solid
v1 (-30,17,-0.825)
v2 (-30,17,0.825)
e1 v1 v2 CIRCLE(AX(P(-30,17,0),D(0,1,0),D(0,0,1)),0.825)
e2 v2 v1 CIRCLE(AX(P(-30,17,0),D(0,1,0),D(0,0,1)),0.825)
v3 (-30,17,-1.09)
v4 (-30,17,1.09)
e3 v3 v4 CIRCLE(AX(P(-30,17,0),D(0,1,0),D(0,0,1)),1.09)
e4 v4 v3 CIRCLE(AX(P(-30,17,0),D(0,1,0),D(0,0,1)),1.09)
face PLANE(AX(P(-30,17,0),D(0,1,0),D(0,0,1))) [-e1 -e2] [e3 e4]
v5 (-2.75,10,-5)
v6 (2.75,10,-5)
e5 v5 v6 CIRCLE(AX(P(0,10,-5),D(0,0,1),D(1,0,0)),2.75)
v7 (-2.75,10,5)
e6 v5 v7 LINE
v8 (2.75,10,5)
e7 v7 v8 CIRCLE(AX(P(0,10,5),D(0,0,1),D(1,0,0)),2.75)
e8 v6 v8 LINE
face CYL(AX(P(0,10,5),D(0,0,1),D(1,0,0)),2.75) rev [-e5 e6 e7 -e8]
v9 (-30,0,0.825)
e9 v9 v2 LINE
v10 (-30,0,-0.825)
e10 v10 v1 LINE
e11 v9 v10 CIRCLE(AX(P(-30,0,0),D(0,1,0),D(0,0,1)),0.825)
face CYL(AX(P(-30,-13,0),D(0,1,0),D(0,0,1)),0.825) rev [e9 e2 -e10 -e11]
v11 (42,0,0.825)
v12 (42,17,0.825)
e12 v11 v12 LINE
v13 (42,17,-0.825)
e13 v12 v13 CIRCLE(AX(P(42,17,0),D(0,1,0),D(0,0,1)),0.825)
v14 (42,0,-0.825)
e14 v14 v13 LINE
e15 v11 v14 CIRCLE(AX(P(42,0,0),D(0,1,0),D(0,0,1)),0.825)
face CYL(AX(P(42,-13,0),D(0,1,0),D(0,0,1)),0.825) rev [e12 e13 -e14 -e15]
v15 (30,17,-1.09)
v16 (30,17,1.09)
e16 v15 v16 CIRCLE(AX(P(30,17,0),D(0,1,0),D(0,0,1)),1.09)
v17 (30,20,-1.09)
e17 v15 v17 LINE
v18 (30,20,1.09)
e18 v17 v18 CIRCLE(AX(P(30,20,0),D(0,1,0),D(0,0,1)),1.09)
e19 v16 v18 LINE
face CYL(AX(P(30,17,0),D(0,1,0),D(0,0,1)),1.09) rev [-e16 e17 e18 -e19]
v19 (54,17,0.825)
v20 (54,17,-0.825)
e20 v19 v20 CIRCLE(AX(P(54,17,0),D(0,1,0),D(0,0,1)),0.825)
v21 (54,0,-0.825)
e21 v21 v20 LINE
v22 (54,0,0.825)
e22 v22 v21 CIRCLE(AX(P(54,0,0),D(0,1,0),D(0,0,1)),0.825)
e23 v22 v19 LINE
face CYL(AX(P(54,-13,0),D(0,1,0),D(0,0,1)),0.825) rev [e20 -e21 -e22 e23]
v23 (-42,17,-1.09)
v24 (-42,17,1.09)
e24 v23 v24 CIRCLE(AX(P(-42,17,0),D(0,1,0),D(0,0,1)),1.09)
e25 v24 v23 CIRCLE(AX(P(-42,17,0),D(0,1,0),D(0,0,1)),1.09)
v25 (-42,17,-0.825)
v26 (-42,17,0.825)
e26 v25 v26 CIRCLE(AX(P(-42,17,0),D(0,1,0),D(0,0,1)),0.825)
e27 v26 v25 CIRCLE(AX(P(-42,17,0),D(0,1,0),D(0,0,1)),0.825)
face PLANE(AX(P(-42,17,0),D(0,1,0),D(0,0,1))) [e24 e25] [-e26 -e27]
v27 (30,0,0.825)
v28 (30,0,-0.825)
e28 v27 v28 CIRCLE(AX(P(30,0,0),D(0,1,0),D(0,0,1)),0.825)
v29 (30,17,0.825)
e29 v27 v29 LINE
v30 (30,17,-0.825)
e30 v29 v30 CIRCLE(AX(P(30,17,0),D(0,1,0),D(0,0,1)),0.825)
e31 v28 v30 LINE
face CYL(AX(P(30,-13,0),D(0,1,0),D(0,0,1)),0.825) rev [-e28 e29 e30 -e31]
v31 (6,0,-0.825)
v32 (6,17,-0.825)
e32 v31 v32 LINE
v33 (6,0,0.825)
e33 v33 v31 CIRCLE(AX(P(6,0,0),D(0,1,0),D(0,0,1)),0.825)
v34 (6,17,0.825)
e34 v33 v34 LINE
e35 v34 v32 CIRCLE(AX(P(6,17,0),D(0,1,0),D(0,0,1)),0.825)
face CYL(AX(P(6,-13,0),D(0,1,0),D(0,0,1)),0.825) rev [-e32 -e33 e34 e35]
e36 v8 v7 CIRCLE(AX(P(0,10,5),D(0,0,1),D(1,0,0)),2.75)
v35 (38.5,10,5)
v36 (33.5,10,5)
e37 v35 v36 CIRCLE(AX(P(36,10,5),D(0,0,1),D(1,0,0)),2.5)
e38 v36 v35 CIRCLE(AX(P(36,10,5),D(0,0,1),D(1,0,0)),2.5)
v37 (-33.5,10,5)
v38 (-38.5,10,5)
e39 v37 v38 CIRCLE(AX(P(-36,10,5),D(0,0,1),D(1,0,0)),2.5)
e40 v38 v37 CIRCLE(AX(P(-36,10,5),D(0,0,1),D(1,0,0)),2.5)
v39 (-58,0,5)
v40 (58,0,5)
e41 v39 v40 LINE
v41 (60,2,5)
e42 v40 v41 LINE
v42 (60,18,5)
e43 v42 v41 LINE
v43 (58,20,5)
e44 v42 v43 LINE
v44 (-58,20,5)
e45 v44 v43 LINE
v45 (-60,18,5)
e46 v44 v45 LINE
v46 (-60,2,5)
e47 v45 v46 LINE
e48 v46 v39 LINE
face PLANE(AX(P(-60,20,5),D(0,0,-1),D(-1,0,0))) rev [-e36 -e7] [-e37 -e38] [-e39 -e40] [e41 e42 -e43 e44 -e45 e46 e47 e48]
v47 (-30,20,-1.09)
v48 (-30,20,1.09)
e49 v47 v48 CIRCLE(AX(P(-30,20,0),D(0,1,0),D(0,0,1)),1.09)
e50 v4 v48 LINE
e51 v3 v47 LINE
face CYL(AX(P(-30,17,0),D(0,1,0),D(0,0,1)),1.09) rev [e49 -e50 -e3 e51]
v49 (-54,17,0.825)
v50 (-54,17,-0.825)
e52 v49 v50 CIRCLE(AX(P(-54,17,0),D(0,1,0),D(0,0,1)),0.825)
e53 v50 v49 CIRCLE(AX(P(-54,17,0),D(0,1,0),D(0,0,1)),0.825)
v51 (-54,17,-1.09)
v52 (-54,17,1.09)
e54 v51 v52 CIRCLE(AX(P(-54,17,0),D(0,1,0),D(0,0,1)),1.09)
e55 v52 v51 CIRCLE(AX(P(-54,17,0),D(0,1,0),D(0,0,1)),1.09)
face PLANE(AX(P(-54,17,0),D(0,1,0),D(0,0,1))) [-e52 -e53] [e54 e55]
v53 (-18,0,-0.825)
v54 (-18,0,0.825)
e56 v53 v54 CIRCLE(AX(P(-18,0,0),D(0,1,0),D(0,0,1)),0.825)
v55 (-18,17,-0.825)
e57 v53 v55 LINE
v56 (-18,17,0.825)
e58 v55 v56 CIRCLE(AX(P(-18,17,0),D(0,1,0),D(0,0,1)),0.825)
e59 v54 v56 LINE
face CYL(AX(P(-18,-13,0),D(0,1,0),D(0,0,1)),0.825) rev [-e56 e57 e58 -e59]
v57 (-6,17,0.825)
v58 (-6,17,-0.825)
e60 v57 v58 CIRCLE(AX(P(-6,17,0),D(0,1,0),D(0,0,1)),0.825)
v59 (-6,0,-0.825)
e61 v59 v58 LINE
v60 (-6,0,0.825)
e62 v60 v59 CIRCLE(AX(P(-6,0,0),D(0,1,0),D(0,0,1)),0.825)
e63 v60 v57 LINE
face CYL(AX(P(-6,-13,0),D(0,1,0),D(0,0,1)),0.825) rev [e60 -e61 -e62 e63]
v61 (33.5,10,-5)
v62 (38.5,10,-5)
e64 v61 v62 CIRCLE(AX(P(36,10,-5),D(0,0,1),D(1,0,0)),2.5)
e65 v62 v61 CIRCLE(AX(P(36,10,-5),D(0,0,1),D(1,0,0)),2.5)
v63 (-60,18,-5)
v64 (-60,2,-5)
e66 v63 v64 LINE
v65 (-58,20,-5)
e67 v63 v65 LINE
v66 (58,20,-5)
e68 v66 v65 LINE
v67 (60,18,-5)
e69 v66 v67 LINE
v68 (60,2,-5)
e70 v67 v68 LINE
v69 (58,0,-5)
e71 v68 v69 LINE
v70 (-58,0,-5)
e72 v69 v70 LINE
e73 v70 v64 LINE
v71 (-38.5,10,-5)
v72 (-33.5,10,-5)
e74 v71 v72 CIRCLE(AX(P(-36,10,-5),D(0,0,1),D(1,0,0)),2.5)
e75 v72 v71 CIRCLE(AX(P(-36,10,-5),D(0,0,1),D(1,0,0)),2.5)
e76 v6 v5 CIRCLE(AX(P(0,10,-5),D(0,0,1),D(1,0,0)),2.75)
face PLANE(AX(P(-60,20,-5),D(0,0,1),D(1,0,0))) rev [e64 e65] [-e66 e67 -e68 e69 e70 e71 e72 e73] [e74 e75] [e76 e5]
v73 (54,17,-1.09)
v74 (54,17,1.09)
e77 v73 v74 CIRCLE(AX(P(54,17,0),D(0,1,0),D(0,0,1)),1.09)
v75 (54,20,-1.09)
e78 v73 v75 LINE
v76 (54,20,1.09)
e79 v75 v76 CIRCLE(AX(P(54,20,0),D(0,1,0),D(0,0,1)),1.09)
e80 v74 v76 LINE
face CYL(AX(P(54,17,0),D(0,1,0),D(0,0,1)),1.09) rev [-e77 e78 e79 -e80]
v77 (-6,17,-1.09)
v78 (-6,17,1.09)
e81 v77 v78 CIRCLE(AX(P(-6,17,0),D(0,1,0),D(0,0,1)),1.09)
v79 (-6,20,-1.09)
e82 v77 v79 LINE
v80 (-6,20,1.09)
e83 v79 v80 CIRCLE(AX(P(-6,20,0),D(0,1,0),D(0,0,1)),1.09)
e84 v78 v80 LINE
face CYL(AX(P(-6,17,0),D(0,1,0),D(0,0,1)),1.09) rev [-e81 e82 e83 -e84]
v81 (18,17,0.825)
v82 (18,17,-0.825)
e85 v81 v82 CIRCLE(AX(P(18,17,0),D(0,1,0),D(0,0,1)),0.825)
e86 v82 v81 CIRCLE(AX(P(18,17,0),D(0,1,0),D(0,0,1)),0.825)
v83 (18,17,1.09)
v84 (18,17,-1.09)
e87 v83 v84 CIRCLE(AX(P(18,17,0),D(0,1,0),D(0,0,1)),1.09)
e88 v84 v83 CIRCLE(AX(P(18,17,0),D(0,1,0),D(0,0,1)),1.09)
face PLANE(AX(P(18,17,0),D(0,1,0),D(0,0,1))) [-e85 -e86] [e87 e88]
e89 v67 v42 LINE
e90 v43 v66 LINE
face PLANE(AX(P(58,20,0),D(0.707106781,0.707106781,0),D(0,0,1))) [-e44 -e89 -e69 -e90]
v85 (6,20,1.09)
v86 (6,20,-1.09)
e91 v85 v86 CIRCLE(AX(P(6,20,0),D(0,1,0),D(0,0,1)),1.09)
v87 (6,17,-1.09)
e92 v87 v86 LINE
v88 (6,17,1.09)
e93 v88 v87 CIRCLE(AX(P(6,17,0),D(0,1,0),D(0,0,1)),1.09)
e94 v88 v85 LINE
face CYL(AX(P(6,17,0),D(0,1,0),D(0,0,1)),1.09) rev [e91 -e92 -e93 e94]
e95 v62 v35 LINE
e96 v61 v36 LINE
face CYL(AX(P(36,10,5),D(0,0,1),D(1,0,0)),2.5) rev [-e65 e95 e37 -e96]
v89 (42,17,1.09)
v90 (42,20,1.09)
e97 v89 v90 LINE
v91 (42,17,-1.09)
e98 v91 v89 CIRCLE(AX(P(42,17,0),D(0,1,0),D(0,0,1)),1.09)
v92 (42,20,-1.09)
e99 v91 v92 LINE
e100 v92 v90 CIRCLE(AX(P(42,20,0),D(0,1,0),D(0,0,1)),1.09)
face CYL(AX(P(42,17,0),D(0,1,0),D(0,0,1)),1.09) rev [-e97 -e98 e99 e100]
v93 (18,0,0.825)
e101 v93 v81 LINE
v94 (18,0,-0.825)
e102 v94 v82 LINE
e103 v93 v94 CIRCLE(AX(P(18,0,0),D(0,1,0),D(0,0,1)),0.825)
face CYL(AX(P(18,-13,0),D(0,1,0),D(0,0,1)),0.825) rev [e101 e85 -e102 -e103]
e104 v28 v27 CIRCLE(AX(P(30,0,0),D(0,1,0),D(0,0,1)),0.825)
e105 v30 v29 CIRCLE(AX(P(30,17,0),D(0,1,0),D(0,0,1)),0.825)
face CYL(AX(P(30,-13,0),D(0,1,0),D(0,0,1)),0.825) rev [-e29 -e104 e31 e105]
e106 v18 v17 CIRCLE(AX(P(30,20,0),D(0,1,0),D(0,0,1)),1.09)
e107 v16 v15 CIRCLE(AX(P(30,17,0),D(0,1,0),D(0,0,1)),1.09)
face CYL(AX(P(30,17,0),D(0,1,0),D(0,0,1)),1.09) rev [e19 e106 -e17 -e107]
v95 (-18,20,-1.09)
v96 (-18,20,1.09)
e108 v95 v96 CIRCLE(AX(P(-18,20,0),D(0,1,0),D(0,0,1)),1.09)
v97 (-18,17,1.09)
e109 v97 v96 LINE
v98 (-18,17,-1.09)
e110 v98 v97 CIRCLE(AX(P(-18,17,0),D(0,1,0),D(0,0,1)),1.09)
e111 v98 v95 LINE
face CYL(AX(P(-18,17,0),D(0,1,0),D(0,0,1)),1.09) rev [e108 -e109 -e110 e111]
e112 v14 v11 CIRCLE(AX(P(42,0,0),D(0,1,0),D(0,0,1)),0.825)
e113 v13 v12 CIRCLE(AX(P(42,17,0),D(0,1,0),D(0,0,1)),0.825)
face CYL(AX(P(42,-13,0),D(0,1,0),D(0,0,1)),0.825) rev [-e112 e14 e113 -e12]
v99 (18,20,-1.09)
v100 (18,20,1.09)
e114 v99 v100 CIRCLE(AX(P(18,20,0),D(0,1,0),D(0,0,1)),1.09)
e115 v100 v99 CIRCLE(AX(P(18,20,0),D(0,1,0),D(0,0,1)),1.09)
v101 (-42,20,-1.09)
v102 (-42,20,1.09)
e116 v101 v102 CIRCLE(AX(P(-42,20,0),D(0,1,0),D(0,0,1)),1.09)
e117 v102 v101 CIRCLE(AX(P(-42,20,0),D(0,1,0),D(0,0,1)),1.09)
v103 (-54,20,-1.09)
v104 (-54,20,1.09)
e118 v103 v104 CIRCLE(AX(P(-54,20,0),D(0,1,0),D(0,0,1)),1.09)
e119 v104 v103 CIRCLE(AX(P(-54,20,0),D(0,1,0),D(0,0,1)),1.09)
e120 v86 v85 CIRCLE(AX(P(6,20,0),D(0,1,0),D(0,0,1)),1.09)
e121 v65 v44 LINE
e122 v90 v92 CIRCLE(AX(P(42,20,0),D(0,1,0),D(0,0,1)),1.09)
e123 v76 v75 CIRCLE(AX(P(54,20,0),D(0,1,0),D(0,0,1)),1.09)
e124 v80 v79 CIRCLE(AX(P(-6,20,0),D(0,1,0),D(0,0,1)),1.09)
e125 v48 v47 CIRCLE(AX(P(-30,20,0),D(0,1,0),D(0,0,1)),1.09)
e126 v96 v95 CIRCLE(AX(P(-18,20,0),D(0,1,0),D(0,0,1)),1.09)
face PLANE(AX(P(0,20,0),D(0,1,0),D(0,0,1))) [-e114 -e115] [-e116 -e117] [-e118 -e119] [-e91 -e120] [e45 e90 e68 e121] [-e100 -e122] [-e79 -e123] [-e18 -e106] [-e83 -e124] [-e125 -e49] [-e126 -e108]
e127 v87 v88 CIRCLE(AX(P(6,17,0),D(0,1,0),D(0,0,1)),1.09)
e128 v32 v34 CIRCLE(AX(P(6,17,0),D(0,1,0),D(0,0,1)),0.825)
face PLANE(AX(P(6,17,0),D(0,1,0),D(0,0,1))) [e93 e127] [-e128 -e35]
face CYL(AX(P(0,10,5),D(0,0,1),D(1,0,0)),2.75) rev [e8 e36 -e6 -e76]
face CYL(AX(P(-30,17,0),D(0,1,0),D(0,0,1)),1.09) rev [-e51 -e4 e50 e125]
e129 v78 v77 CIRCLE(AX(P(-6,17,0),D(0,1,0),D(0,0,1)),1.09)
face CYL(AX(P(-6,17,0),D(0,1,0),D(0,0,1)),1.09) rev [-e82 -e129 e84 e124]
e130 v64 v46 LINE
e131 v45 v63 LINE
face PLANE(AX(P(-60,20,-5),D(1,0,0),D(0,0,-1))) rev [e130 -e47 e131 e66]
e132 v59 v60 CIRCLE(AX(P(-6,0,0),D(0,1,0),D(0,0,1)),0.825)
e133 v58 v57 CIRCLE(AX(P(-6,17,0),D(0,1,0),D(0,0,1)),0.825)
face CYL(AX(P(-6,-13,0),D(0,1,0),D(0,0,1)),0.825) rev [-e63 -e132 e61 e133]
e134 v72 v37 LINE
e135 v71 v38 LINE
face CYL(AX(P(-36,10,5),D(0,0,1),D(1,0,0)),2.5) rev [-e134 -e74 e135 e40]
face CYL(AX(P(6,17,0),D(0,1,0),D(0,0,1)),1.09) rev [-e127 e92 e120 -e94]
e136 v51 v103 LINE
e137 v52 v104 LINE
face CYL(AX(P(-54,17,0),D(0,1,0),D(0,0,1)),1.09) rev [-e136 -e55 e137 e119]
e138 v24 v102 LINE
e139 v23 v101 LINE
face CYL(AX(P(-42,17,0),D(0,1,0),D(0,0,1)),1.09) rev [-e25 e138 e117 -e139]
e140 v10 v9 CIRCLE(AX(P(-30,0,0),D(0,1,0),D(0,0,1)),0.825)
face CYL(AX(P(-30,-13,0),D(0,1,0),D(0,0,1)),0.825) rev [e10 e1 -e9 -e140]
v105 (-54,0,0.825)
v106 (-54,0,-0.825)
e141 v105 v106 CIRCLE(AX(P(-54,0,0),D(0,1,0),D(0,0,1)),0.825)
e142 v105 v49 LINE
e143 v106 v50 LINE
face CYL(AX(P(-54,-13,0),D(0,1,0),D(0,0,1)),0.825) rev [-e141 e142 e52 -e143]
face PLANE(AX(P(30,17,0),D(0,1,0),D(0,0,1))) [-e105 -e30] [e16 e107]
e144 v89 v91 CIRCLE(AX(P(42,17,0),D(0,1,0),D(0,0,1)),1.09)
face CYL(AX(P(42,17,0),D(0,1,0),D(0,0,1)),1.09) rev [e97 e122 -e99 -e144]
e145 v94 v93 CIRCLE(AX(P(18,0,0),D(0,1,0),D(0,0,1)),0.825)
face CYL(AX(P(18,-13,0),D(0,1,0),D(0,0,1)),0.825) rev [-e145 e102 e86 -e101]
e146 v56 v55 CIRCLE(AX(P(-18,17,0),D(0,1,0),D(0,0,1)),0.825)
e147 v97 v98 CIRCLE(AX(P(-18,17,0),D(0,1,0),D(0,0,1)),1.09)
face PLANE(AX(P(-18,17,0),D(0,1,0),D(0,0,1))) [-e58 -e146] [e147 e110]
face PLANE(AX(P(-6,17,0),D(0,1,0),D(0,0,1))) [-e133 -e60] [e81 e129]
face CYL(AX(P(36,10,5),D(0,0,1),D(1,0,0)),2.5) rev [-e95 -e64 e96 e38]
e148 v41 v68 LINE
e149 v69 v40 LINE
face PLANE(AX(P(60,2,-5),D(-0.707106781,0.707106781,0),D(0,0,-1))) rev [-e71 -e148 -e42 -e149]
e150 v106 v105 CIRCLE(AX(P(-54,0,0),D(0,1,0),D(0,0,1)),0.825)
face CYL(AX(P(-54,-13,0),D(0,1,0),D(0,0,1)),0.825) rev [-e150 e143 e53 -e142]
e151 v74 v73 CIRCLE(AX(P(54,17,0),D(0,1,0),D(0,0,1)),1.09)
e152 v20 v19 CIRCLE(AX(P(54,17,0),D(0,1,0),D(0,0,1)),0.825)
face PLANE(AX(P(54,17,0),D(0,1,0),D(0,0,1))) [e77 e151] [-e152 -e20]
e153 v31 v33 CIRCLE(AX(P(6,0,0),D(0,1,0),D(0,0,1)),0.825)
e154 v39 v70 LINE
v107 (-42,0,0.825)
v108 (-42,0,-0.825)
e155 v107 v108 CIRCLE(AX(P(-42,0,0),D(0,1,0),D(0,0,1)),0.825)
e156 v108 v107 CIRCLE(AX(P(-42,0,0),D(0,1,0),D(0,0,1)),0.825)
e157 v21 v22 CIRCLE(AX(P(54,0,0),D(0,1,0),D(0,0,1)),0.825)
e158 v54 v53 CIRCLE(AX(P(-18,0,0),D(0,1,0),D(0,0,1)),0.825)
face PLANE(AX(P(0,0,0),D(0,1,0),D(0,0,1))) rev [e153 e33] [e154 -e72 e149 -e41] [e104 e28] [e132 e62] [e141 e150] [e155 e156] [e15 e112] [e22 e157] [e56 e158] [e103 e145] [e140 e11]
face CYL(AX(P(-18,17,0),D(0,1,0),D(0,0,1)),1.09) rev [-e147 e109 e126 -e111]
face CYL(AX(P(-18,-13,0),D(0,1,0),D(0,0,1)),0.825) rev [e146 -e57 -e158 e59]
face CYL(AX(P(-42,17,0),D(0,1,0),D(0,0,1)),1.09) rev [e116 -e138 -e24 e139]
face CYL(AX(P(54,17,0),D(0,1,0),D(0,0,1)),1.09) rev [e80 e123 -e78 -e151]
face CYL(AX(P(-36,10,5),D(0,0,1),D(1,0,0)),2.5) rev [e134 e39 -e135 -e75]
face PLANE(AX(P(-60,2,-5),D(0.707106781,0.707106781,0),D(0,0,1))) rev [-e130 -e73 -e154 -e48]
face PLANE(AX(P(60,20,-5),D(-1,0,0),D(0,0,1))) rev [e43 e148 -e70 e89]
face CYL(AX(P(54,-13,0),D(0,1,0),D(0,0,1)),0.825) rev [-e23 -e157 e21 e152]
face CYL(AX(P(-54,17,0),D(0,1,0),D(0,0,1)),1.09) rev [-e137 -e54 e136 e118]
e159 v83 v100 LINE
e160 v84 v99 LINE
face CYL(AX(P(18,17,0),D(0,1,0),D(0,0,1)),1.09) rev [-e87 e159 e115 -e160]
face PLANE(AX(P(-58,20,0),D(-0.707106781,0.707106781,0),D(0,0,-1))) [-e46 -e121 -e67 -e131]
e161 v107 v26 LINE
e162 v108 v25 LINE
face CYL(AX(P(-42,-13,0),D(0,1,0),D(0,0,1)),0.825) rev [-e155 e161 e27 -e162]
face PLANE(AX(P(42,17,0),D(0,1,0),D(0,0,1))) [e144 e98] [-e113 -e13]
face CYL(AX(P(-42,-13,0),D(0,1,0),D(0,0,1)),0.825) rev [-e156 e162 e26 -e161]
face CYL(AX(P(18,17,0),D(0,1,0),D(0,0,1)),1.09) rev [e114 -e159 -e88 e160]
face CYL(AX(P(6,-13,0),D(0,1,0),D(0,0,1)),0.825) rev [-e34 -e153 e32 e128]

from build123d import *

# Parameters (mm, degrees)
SKETCH_1_W             = 120
SKETCH_1_H             = 10
EXTRUDE_1_DEPTH        = 20
SKETCH_2_R             = 1.09
CUT_EXTRUDE_1_DEPTH    = 3
SKETCH_4_R             = 0.825
CUT_EXTRUDE_2_DEPTH    = 30
PATTERN_LINEAR_1_COUNT = 10
PATTERN_LINEAR_1_PITCH = 12
CHAMFER_1_SIZE         = 2
MM_1_D                 = 5
MM_1_DEPTH             = 15
MM_1_TIP               = 1.502151548
HOLE_WIZARD_M5_1_D     = 5.5
HOLE_WIZARD_M5_1_DEPTH = 15
HOLE_WIZARD_M5_1_TIP   = 1.652366702


with BuildPart() as part:
    # 草图1 → 凸台-拉伸1 (new body)
    with BuildSketch(Plane(origin=(0, 0, 0), x_dir=(1, 0, 0), z_dir=(0, 1, 0))):
        Rectangle(SKETCH_1_W, SKETCH_1_H)
    extrude(amount=EXTRUDE_1_DEPTH)

    # 草图2 → 切除-拉伸1 (cut)
    with BuildSketch(Plane(origin=(0, 20, 0), x_dir=(1, 0, 0), z_dir=(0, 1, 0))):
        with Locations(Location((-54, 0, 0), (0, 0, 270))):
            Circle(SKETCH_2_R)
    cut_extrude_1 = extrude(amount=-CUT_EXTRUDE_1_DEPTH, mode=Mode.SUBTRACT)

    # 草图4 → 切除-拉伸2 (cut)
    with BuildSketch(Plane(origin=(0, 17, 0), x_dir=(1, 0, 0), z_dir=(0, 1, 0))):
        with Locations(Location((-54, 0, 0), (0, 0, 270))):
            Circle(SKETCH_4_R)
    cut_extrude_2 = extrude(amount=-CUT_EXTRUDE_2_DEPTH, mode=Mode.SUBTRACT)

    # 阵列(线性)1: 切除-拉伸1, 切除-拉伸2 ×10
    with Locations(*[(i * PATTERN_LINEAR_1_PITCH, 0, 0) for i in range(1, PATTERN_LINEAR_1_COUNT)]):
        add(cut_extrude_1, mode=Mode.SUBTRACT)
        add(cut_extrude_2, mode=Mode.SUBTRACT)

    # 倒角1
    chamfer_1_edges = [part.edges().sort_by_distance(p)[0] for p in [
        (-60, 20, 0),
        (60, 20, 0),
        (-60, 0, 0),
        (60, 0, 0),
    ]]
    chamfer(chamfer_1_edges, length=CHAMFER_1_SIZE)

    # 大小mm 暗销孔1
    with Locations(Plane.XY.offset(5)):
        with Locations((36, 10), (-36, 10)):
            Hole(MM_1_D / 2, depth=MM_1_DEPTH)
            with Locations((0, 0, -(MM_1_DEPTH + MM_1_TIP / 2))):  # 118° drill point
                Cone(0, MM_1_D / 2, MM_1_TIP, mode=Mode.SUBTRACT)

    # M5 间隙孔1
    with Locations(Plane.XY.offset(5)):
        with Locations((0, 10)):
            Hole(HOLE_WIZARD_M5_1_D / 2, depth=HOLE_WIZARD_M5_1_DEPTH)
            with Locations((0, 0, -(HOLE_WIZARD_M5_1_DEPTH + HOLE_WIZARD_M5_1_TIP / 2))):  # 118° drill point
                Cone(0, HOLE_WIZARD_M5_1_D / 2, HOLE_WIZARD_M5_1_TIP, mode=Mode.SUBTRACT)


solid = part.part
